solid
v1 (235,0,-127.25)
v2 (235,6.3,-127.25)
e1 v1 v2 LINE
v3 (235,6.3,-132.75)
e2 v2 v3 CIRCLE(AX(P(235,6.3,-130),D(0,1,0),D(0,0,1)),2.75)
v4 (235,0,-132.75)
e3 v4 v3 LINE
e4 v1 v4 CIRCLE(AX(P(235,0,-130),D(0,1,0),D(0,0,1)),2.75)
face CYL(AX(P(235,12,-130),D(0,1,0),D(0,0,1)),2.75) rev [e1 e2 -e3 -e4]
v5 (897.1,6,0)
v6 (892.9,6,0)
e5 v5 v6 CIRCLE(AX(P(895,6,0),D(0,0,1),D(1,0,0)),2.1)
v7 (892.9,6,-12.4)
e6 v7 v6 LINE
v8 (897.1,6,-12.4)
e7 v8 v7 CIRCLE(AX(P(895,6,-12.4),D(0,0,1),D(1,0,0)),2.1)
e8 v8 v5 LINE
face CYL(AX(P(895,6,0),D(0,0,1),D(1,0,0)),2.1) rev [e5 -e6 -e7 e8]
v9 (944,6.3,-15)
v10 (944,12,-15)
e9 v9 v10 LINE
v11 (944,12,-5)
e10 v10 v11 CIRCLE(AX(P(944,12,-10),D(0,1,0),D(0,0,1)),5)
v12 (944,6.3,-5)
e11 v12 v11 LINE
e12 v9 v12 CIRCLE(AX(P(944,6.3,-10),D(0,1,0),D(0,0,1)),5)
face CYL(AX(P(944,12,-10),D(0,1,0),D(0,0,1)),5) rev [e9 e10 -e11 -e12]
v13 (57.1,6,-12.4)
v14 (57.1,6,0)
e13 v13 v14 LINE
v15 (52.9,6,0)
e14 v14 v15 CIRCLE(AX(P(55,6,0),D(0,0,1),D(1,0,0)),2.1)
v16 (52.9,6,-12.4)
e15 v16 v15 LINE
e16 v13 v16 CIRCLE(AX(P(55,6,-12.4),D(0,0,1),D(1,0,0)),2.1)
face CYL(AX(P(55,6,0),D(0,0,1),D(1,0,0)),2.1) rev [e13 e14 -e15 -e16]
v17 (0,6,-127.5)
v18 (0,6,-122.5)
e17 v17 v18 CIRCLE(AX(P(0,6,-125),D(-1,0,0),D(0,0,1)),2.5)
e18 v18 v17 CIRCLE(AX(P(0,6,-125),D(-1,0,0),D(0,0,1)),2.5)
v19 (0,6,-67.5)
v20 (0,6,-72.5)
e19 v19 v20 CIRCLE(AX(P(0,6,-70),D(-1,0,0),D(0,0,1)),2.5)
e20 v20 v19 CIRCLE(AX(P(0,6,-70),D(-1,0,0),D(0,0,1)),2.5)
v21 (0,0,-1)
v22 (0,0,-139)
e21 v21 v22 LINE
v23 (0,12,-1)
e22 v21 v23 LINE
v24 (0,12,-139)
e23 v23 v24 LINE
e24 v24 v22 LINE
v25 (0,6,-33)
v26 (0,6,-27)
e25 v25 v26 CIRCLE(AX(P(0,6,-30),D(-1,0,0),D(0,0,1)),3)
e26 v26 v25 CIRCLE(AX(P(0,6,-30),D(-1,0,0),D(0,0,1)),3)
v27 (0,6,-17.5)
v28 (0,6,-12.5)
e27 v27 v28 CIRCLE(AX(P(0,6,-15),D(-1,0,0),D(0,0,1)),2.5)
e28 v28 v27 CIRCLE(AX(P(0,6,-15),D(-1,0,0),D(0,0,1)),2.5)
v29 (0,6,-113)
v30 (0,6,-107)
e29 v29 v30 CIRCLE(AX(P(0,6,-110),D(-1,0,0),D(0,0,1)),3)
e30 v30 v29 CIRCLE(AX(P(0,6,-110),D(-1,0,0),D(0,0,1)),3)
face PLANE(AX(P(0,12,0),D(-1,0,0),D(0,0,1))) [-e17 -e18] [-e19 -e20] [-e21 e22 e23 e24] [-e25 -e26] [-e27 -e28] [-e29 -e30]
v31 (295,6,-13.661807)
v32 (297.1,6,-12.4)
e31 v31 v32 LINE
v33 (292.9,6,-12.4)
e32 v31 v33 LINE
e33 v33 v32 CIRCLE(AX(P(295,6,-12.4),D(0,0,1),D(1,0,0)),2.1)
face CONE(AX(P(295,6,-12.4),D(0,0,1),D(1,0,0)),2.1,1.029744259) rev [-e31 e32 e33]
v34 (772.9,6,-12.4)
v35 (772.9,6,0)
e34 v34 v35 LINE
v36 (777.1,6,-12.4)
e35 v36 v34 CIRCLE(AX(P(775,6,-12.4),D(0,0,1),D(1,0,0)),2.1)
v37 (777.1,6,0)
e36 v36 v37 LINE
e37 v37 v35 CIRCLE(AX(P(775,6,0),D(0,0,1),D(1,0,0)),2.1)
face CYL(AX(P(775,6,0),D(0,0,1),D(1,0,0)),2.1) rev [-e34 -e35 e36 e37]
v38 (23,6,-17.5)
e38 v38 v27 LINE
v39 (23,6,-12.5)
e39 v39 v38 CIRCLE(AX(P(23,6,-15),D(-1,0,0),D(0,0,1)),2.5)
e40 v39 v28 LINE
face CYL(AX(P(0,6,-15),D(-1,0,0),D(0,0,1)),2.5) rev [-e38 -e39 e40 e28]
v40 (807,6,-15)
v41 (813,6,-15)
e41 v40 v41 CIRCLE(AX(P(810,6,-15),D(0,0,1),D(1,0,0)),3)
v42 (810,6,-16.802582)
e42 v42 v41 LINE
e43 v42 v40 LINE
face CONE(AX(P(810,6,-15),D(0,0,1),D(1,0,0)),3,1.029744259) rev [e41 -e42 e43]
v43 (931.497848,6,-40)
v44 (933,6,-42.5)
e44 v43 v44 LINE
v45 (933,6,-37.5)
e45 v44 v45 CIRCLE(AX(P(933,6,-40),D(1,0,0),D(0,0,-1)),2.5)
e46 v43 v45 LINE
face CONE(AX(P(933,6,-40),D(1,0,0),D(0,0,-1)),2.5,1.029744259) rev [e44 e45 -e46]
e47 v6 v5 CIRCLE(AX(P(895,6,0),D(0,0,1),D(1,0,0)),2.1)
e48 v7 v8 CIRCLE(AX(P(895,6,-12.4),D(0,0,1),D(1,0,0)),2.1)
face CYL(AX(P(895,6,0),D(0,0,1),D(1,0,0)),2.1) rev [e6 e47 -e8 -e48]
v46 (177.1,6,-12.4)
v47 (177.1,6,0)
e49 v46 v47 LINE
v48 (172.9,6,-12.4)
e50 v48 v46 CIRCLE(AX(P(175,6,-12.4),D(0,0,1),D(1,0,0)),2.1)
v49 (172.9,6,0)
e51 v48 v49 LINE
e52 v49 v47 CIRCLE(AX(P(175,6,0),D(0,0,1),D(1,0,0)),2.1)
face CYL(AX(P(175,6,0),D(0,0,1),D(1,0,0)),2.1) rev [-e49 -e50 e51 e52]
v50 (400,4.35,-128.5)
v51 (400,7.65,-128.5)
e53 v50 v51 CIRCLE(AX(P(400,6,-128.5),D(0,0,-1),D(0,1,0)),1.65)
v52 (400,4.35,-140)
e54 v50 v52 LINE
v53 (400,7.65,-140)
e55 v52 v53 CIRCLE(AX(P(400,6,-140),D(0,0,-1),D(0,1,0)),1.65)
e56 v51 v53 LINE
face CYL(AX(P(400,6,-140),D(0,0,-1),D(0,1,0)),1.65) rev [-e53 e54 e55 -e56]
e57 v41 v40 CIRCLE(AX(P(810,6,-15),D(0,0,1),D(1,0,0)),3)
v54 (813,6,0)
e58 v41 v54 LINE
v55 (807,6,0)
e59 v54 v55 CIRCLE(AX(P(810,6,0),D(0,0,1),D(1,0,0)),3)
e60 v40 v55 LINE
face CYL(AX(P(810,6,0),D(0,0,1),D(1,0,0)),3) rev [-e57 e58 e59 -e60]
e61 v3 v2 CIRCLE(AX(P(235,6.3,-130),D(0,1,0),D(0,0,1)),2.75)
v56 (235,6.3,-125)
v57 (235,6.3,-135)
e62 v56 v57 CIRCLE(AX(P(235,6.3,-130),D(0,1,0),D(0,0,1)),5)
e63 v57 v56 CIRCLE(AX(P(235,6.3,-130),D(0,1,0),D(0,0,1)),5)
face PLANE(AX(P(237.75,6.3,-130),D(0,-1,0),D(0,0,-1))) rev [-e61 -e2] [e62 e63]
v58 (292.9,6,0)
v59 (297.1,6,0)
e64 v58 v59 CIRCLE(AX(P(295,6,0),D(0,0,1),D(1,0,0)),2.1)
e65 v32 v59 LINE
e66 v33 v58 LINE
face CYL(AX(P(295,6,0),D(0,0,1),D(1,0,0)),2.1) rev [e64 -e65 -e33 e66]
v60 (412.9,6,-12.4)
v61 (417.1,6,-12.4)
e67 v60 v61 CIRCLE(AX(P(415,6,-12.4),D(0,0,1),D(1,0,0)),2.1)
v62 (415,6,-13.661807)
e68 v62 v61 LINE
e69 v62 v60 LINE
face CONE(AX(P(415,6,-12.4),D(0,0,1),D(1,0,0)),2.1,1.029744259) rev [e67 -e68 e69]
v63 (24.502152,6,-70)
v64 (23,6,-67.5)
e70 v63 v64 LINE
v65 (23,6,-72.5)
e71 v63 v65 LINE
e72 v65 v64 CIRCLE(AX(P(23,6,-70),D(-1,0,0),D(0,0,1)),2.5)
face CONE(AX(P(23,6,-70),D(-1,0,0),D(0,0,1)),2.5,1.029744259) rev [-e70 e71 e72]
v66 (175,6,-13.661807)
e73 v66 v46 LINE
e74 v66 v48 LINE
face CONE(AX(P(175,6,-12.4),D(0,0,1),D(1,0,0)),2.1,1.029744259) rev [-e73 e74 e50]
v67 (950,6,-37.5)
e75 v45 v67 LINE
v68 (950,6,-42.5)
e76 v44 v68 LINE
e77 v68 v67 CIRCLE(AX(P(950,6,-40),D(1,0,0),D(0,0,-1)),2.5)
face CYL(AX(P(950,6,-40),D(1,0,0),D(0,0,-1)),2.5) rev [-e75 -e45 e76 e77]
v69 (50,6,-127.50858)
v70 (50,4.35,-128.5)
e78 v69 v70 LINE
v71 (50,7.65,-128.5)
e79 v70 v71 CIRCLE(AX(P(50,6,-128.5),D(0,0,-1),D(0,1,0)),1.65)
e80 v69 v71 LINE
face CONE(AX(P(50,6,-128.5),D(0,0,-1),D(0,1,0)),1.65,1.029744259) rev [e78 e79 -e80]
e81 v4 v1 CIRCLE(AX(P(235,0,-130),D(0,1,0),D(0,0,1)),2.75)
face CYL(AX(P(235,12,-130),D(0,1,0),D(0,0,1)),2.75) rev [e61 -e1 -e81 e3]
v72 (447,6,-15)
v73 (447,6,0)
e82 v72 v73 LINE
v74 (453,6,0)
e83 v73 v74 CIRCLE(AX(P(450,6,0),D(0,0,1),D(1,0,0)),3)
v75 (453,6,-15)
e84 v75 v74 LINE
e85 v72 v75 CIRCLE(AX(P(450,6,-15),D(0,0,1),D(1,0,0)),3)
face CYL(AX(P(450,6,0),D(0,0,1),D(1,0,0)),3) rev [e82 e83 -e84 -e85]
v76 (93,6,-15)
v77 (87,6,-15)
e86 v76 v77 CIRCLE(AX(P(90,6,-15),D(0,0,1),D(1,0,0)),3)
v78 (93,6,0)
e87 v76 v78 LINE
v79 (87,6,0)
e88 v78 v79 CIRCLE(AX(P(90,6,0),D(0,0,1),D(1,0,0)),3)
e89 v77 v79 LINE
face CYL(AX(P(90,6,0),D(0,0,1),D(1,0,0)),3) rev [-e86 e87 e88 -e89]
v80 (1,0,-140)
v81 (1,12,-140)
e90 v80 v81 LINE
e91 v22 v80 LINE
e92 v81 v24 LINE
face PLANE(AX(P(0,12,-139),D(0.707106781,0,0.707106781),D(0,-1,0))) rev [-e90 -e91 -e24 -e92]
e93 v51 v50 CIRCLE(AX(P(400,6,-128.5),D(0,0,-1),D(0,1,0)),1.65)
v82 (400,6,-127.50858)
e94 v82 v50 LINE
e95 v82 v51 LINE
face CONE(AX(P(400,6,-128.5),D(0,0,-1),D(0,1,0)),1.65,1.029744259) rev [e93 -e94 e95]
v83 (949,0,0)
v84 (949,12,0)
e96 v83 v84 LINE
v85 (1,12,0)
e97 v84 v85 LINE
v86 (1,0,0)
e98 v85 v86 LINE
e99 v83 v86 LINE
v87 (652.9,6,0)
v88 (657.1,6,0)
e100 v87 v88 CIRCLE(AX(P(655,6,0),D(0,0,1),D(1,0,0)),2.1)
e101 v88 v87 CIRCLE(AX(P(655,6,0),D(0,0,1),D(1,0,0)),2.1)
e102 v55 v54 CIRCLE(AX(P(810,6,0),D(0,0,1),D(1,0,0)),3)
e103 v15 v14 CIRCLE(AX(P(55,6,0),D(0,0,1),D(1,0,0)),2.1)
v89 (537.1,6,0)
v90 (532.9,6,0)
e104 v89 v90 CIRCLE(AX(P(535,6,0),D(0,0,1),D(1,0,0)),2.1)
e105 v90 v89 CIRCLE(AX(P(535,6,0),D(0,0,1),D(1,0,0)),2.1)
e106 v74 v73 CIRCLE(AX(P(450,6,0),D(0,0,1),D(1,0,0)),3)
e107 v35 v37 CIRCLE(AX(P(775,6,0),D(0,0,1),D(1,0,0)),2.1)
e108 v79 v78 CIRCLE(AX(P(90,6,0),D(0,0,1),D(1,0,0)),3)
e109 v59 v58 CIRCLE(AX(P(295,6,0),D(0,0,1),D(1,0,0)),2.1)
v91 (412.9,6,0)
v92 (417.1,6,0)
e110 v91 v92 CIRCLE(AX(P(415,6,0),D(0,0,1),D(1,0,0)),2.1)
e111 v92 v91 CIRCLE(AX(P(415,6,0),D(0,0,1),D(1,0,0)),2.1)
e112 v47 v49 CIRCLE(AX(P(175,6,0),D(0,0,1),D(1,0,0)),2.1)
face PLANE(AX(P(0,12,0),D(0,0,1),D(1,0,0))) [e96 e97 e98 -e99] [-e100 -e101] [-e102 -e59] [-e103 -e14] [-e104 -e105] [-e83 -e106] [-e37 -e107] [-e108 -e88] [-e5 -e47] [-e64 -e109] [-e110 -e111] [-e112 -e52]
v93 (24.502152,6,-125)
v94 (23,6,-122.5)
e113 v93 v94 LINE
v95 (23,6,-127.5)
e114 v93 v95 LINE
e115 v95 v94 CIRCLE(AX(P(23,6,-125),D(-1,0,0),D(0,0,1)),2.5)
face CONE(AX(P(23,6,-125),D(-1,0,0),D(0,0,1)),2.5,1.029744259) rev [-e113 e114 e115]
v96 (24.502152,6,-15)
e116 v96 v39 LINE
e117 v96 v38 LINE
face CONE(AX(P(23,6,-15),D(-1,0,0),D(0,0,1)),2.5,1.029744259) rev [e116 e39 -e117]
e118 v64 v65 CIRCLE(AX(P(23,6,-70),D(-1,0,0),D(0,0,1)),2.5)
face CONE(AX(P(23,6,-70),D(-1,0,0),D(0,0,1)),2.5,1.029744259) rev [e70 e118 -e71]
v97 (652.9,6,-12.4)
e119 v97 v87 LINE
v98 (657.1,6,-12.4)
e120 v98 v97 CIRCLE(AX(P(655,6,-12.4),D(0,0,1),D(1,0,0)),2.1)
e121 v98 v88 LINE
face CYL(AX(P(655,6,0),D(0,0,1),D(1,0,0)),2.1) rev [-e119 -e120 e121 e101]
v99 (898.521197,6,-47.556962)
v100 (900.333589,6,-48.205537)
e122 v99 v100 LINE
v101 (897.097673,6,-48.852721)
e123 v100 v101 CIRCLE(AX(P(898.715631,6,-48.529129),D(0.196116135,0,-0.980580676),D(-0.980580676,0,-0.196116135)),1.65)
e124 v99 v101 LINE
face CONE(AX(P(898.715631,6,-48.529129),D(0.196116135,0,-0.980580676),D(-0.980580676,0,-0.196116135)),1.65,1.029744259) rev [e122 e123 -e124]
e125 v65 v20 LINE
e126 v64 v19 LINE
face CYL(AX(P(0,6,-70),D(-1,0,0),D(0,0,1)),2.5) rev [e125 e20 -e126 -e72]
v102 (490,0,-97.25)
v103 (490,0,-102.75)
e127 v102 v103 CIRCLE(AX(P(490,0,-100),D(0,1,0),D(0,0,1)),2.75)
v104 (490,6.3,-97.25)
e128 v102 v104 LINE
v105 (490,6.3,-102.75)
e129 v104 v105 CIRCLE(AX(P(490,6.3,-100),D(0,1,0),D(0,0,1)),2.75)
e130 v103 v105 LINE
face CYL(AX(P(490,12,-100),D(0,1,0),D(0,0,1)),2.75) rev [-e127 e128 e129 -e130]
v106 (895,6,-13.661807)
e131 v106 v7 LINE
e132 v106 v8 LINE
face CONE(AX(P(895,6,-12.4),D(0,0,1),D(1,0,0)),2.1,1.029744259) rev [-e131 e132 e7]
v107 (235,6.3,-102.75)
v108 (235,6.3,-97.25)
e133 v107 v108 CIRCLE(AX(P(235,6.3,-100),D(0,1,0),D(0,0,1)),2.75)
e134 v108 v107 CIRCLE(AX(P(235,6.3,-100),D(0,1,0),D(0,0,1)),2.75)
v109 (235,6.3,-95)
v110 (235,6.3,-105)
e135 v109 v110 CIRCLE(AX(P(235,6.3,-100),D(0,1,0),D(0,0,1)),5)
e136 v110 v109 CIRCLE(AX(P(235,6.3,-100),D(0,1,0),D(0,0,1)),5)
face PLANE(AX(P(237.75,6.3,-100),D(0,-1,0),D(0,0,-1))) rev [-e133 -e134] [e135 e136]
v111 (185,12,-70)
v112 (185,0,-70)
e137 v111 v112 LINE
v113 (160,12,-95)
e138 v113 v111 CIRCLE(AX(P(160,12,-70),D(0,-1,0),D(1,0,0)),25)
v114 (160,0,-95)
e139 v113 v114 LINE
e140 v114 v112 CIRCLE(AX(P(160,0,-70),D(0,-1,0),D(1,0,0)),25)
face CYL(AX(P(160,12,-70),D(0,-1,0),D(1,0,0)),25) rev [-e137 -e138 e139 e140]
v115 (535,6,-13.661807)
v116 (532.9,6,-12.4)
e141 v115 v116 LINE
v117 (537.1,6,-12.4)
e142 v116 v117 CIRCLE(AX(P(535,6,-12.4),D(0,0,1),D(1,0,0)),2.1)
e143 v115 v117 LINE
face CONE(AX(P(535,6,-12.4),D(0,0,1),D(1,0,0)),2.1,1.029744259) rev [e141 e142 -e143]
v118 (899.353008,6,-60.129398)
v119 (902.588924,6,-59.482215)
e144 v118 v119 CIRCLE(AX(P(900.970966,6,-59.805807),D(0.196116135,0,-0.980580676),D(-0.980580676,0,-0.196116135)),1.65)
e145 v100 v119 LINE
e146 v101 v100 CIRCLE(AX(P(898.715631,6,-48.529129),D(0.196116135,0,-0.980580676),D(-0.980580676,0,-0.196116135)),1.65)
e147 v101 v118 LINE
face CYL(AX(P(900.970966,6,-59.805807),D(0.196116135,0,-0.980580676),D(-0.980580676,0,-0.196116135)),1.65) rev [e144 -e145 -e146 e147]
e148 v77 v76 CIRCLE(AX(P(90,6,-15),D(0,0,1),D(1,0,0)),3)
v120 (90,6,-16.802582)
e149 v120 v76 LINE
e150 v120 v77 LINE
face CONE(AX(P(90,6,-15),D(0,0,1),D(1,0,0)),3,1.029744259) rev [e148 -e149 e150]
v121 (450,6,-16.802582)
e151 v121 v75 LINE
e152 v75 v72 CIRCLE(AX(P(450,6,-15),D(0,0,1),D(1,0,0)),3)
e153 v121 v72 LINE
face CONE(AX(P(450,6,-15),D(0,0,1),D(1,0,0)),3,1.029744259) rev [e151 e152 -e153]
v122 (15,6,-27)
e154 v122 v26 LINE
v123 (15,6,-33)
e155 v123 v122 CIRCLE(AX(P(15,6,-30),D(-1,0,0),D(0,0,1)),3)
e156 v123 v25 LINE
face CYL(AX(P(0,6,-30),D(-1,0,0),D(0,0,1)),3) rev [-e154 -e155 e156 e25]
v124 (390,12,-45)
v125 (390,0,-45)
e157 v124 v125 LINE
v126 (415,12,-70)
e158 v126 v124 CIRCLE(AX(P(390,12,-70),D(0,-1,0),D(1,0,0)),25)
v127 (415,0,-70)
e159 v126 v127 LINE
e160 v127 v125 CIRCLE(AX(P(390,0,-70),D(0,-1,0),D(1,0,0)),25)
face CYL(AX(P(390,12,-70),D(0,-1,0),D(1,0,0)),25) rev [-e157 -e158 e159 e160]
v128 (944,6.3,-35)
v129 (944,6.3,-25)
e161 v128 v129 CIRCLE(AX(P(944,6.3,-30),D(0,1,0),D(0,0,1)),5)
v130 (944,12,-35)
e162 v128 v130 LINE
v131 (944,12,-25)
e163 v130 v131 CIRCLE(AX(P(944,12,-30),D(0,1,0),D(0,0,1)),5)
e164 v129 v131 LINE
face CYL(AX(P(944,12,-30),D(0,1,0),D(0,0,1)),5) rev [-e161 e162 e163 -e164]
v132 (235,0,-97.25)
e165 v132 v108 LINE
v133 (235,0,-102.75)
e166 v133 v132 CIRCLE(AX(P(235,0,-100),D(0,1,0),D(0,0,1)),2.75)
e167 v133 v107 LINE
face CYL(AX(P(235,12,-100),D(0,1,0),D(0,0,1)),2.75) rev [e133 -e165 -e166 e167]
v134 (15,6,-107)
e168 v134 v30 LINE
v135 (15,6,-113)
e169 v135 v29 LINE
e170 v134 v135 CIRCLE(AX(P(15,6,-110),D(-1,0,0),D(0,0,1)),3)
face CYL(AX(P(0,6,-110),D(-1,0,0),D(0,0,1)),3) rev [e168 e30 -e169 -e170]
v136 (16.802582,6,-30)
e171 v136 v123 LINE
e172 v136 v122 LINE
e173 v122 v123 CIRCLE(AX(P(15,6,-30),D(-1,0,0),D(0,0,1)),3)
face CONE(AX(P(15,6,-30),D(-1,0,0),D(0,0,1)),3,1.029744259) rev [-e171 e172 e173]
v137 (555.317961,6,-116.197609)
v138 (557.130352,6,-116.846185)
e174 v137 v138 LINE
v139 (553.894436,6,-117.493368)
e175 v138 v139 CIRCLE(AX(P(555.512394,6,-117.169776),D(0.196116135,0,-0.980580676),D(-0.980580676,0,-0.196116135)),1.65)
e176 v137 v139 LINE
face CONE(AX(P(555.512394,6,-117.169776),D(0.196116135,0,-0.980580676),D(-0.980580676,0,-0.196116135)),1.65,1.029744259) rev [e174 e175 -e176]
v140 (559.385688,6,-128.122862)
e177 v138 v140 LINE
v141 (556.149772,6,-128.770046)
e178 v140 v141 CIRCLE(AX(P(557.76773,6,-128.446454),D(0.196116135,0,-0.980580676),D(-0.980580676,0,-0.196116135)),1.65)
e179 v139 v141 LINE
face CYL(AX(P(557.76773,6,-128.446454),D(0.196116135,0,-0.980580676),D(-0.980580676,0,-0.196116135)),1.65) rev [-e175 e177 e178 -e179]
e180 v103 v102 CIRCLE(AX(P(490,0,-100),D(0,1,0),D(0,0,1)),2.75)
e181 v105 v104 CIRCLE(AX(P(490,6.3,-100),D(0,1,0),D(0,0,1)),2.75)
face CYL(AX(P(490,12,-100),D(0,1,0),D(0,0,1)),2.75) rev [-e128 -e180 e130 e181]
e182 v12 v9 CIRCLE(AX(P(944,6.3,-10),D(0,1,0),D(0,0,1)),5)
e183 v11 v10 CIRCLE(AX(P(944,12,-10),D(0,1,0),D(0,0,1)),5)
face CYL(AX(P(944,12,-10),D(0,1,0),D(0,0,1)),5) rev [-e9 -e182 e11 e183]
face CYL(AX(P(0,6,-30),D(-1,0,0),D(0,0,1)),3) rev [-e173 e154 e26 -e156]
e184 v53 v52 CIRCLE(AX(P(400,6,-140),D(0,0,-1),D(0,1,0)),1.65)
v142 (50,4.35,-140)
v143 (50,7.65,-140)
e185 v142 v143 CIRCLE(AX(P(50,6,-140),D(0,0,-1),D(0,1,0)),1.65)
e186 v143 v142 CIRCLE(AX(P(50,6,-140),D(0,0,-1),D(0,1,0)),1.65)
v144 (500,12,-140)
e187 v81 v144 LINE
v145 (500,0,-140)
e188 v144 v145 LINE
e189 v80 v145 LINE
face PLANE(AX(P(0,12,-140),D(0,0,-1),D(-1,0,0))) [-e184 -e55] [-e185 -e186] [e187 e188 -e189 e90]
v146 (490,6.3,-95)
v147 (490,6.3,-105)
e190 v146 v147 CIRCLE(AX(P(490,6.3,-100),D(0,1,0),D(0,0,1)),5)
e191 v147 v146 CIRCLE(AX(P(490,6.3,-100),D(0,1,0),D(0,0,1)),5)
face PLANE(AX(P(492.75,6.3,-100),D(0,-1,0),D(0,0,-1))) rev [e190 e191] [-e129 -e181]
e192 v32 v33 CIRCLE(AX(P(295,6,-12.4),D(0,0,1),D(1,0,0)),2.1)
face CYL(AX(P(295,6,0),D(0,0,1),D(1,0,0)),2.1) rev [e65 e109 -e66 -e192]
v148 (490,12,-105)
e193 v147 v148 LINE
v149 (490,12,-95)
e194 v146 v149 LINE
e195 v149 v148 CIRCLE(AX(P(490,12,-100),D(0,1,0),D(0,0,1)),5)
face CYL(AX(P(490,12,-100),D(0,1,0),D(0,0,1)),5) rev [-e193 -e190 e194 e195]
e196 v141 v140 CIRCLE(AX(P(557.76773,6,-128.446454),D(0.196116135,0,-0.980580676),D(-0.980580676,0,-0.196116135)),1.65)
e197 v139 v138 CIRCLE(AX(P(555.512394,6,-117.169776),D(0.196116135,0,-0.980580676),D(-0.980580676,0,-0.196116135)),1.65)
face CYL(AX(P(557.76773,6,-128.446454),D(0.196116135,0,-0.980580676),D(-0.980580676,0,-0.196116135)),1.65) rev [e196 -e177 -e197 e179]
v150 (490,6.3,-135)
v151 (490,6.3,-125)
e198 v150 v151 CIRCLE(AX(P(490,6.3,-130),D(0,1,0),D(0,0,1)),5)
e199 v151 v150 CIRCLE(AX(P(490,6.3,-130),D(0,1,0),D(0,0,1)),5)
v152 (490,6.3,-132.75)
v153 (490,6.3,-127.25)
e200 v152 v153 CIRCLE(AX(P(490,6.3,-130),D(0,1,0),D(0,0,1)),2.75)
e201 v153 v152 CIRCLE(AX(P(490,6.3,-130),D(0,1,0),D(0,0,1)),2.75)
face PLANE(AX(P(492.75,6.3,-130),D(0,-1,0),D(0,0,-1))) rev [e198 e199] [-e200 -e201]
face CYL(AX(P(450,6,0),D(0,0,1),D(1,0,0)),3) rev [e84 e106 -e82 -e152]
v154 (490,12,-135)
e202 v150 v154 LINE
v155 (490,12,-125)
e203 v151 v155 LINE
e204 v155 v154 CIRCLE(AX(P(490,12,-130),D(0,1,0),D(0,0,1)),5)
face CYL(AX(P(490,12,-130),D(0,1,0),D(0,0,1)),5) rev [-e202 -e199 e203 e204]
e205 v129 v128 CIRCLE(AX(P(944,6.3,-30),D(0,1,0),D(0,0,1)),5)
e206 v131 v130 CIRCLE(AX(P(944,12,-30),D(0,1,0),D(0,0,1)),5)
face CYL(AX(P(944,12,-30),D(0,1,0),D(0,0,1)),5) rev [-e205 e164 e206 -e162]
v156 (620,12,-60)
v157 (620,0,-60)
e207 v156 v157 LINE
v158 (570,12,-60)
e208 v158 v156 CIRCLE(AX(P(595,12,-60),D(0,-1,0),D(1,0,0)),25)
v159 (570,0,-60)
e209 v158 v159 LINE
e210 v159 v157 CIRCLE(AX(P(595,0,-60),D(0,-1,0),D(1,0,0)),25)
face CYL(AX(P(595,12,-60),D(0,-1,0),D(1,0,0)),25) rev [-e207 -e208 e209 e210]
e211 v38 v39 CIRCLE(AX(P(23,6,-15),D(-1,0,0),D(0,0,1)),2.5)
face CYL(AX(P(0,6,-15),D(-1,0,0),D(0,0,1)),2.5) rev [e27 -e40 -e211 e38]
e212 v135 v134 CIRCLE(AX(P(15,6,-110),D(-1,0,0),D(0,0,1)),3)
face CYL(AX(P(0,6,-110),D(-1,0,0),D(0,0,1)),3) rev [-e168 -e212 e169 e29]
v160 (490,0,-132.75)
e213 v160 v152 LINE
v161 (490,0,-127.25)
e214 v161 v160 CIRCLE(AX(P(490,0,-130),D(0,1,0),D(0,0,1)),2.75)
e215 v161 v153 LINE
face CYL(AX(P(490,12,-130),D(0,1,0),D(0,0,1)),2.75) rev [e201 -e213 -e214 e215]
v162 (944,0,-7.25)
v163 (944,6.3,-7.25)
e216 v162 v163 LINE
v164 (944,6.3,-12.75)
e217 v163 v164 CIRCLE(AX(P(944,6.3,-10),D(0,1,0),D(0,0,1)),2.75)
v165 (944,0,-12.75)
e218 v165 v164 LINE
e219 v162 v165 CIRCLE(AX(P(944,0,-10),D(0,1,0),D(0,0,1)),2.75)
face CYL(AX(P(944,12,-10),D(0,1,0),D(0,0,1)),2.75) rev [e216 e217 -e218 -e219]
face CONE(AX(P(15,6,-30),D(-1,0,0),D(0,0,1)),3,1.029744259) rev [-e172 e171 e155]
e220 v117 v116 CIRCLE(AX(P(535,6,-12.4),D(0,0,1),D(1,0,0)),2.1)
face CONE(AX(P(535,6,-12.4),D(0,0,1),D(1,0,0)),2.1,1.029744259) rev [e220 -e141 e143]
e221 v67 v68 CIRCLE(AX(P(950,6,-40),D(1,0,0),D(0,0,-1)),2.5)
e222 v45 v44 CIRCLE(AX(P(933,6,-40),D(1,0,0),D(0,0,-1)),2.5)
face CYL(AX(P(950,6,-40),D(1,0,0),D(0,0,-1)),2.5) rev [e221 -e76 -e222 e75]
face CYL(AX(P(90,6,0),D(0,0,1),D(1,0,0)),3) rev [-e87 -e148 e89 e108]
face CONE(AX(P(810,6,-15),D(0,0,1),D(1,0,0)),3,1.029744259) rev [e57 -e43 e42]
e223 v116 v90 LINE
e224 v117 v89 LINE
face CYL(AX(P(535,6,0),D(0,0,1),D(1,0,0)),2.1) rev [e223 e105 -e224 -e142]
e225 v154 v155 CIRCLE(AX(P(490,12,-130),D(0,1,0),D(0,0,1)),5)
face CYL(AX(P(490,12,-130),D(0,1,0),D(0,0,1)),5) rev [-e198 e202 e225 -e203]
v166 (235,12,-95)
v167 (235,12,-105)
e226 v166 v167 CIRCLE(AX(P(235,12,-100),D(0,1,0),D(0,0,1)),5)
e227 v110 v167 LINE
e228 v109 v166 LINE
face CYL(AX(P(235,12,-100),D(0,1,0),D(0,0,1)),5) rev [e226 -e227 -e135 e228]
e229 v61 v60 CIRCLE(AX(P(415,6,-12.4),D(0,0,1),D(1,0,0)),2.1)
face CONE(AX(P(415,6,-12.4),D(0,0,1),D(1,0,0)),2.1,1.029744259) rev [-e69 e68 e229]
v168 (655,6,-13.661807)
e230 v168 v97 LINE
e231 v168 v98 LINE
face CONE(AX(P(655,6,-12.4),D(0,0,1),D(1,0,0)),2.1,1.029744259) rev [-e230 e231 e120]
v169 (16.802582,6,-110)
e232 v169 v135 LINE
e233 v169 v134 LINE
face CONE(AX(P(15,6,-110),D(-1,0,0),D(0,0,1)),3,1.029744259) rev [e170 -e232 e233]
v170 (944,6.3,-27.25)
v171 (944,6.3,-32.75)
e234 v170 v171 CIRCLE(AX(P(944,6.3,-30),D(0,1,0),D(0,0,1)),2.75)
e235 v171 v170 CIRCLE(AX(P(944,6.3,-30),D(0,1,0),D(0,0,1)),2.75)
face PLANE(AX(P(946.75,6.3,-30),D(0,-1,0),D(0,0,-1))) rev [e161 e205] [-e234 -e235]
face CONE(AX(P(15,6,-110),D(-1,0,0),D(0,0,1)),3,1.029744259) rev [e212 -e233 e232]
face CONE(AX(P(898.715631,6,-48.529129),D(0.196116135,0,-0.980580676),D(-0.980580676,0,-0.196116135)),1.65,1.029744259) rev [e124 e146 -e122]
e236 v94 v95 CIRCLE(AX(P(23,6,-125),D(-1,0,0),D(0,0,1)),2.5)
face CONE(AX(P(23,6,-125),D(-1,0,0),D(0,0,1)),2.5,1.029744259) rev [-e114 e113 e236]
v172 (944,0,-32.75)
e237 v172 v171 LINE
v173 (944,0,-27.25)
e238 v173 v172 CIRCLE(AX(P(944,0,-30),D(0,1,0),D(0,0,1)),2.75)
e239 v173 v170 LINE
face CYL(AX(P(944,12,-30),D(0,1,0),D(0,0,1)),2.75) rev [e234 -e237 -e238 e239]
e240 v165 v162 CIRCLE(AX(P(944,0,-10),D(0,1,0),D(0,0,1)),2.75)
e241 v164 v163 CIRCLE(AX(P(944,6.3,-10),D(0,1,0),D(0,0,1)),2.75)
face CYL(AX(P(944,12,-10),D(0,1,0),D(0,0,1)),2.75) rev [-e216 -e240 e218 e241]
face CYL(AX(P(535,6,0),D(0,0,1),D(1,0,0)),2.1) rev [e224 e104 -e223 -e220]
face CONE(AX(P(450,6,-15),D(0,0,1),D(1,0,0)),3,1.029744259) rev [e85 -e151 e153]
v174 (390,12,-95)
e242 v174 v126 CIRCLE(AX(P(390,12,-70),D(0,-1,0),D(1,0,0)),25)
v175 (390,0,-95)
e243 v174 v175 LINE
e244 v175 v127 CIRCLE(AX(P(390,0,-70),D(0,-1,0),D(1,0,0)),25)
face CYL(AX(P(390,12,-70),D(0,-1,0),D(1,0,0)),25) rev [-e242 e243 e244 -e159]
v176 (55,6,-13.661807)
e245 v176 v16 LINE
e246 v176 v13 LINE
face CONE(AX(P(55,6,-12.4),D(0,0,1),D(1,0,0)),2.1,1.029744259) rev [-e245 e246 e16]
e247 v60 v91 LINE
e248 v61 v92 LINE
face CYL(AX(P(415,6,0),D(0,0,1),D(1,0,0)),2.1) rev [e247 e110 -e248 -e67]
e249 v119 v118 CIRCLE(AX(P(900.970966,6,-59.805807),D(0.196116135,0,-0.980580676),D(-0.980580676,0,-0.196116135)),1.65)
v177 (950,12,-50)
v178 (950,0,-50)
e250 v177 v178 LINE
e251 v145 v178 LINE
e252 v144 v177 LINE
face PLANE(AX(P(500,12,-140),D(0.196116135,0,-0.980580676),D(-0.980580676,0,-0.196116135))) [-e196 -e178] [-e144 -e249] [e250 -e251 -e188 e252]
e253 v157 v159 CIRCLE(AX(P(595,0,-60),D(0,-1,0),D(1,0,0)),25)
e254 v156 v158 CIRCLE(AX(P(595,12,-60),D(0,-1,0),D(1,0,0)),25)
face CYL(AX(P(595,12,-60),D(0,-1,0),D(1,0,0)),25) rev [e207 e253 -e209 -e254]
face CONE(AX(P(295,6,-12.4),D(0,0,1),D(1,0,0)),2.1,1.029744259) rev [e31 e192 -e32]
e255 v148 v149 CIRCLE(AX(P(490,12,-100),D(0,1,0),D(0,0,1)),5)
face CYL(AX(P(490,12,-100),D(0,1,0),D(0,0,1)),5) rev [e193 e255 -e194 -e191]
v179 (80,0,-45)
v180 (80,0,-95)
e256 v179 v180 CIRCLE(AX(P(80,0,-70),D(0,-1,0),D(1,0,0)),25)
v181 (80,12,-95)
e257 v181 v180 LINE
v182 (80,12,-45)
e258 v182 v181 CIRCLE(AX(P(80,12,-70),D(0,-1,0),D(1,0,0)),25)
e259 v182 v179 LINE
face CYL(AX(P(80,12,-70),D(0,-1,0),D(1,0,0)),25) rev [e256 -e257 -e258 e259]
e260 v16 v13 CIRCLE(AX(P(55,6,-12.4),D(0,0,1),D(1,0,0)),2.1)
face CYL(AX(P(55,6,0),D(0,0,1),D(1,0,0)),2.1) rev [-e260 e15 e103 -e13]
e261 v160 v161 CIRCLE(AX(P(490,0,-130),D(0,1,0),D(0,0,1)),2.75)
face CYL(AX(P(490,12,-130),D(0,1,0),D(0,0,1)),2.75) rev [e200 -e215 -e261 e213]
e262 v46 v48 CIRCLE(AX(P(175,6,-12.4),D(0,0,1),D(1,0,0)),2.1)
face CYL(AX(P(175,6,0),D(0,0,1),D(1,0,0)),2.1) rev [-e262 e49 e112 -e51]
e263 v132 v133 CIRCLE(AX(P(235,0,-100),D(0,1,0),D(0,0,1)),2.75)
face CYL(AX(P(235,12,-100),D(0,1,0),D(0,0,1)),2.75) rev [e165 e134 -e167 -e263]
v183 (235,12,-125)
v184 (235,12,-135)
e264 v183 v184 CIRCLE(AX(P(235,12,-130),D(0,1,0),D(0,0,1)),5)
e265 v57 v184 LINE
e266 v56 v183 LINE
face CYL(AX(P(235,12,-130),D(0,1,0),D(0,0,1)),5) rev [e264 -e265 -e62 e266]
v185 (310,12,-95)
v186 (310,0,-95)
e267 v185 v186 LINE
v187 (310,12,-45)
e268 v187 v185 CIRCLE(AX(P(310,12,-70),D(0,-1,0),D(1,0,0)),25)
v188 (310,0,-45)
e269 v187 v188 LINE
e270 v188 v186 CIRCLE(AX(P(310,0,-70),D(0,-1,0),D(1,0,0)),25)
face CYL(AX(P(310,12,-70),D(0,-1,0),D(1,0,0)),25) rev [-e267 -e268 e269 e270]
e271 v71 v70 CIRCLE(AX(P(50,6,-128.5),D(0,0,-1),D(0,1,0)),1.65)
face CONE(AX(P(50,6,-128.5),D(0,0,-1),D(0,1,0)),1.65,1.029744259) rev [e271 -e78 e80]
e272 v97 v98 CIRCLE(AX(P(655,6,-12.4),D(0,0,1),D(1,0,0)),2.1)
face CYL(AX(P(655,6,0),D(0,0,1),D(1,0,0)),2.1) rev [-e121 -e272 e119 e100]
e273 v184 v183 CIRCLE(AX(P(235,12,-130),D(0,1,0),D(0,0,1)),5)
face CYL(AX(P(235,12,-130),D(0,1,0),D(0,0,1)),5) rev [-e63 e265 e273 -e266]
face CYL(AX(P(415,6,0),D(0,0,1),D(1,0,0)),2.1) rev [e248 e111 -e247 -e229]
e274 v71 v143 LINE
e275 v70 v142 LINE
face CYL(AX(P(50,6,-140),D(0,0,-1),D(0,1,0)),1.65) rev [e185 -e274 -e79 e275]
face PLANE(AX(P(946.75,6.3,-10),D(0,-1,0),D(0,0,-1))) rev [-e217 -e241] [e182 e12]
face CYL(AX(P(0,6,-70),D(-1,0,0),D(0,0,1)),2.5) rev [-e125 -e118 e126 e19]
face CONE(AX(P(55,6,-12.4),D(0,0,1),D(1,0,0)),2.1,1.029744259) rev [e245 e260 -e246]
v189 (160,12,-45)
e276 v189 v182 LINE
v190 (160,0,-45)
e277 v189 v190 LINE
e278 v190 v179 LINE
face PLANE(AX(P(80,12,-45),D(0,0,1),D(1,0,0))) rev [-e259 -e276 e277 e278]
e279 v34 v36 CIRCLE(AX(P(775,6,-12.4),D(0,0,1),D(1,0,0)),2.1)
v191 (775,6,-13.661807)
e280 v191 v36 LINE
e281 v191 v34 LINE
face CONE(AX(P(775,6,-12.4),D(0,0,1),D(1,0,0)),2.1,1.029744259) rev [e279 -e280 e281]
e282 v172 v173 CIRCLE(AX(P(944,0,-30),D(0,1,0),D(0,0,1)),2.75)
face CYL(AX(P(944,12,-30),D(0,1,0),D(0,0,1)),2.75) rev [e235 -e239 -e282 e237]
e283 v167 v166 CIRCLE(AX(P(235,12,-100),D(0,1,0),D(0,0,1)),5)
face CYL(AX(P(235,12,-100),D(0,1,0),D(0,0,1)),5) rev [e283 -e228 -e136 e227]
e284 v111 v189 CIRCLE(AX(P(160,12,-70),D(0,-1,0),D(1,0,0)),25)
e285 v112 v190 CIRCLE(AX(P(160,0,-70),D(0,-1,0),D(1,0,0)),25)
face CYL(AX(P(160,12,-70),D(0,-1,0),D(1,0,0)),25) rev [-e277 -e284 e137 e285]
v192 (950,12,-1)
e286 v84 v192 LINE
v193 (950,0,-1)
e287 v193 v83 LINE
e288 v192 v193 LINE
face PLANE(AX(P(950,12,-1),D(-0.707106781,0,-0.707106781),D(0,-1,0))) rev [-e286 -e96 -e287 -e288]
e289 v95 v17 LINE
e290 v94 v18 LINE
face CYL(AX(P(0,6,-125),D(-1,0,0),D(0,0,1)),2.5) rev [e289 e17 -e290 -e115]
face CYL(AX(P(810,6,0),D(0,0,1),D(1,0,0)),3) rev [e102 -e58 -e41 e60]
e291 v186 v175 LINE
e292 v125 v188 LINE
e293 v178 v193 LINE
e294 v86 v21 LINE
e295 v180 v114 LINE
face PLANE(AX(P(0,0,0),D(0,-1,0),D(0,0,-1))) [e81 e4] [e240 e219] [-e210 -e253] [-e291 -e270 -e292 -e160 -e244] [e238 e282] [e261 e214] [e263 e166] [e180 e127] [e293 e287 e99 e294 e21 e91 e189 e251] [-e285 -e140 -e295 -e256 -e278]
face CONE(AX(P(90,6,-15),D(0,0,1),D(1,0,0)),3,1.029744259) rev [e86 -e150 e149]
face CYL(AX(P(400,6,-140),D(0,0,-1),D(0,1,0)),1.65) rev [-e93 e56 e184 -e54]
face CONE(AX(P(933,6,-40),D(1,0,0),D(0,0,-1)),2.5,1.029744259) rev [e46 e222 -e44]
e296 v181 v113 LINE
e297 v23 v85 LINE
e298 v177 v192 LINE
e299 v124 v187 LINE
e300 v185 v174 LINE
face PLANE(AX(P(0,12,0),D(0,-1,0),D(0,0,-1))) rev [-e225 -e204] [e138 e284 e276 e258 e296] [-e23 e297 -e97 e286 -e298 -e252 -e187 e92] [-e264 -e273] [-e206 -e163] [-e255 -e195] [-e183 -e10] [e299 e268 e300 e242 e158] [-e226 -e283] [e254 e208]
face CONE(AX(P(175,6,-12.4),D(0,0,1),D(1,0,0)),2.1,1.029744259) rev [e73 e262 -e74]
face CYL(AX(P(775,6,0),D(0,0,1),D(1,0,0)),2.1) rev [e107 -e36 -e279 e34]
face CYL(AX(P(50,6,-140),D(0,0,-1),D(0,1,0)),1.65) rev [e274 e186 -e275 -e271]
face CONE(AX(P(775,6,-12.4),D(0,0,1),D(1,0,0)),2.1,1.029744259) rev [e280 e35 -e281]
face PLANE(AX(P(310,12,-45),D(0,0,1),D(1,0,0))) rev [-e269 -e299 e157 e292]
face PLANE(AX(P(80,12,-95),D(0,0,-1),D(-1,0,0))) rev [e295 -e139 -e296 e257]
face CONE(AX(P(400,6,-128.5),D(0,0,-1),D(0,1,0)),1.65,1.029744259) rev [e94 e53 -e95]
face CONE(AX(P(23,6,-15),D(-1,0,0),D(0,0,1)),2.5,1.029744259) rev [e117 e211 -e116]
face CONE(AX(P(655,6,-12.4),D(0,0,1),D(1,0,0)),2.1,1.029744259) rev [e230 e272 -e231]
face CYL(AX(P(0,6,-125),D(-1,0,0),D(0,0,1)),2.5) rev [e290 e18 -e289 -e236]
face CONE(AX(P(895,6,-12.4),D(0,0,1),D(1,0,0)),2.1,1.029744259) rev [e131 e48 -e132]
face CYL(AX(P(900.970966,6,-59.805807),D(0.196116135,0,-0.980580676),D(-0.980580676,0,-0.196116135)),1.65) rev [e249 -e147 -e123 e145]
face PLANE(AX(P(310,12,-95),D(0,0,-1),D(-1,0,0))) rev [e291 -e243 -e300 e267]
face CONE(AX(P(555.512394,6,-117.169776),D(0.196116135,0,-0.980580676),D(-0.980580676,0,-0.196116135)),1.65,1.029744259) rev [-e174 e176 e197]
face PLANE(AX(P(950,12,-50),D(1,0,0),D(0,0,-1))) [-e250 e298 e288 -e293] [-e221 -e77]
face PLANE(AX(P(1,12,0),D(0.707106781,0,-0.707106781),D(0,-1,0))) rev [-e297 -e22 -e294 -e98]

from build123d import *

# Parameters (mm, degrees)
BOSS_EXTRUDE2_DEPTH                              = 12
SKETCH9_R                                        = 25
CUT_EXTRUDE3_DEPTH                               = 12
M4_TAPPED_HOLE3_D                                = 3.3
M4_TAPPED_HOLE3_DEPTH                            = 11.5
M4_TAPPED_HOLE3_TIP                              = 0.991420021
M4_TAPPED_HOLE4_D                                = 3.3
M4_TAPPED_HOLE4_DEPTH                            = 11.5
M4_TAPPED_HOLE4_TIP                              = 0.991420021
M6_TAPPED_HOLE3_D                                = 5
M6_TAPPED_HOLE3_DEPTH                            = 17
M6_TAPPED_HOLE3_TIP                              = 1.502151548
M6_TAPPED_HOLE2_D                                = 5
M6_TAPPED_HOLE2_DEPTH                            = 23
M6_TAPPED_HOLE2_TIP                              = 1.502151548
F_6_0_6_DIAMETER_HOLE1_D                         = 6
F_6_0_6_DIAMETER_HOLE1_DEPTH                     = 15
F_6_0_6_DIAMETER_HOLE1_TIP                       = 1.802581857
M5_TAPPED_HOLE1_D                                = 4.2
M5_TAPPED_HOLE1_DEPTH                            = 12.4
M5_TAPPED_HOLE1_TIP                              = 1.2618073
F_6_0_6_DIAMETER_HOLE2_D                         = 6
F_6_0_6_DIAMETER_HOLE2_DEPTH                     = 15
F_6_0_6_DIAMETER_HOLE2_TIP                       = 1.802581857
HOLE_SIZE_PER_HEX_SOCKET_SCREW_TYPE1_D           = 5.5
HOLE_SIZE_PER_HEX_SOCKET_SCREW_TYPE1_CBORE_D     = 10
HOLE_SIZE_PER_HEX_SOCKET_SCREW_TYPE1_CBORE_DEPTH = 5.7
CHAMFER1_SIZE                                    = 1


with BuildPart() as part:
    # Sketch2 → Boss-Extrude2 (new body)
    with BuildSketch(Plane(origin=(0, 0, 0), x_dir=(-1, 0, 0), z_dir=(0, -1, 0))):
        Polygon((0, 0), (0, 140), (-500, 140), (-950, 50), (-950, 0), align=None)
    extrude(amount=-BOSS_EXTRUDE2_DEPTH)

    # Sketch9 → Cut-Extrude3 (cut)
    with BuildSketch(Plane.XZ):
        with Locations((595, -60)):
            Circle(SKETCH9_R)
        with BuildLine():
            Line((80, -45), (160, -45))
            ThreePointArc((160, -45), (185, -70), (160, -95))
            Line((160, -95), (80, -95))
            ThreePointArc((80, -95), (55, -70), (80, -45))
        make_face()
        with BuildLine():
            Line((310, -45), (390, -45))
            ThreePointArc((390, -45), (415, -70), (390, -95))
            Line((390, -95), (310, -95))
            ThreePointArc((310, -95), (285, -70), (310, -45))
        make_face()
    extrude(amount=-CUT_EXTRUDE3_DEPTH, mode=Mode.SUBTRACT)

    # M4 Tapped Hole3
    with Locations(Plane(origin=(0, 0, -140), x_dir=(-1, 0, 0), z_dir=(0, 0, -1))):
        with Locations((-50, 6), (-400, 6)):
            Hole(M4_TAPPED_HOLE3_D / 2, depth=M4_TAPPED_HOLE3_DEPTH)
            with Locations((0, 0, -(M4_TAPPED_HOLE3_DEPTH + M4_TAPPED_HOLE3_TIP / 2))):  # 118° drill point
                Cone(0, M4_TAPPED_HOLE3_D / 2, M4_TAPPED_HOLE3_TIP, mode=Mode.SUBTRACT)

    # M4 Tapped Hole4
    with Locations(Plane(origin=(46.153846154, 0, -230.769230769), x_dir=(-0.9805806756909201, 0, -0.19611613513818424), z_dir=(0.19611613513818424, 0, -0.9805806756909201))):
        with Locations((-871.745835149, 6), (-521.745835149, 6)):
            Hole(M4_TAPPED_HOLE4_D / 2, depth=M4_TAPPED_HOLE4_DEPTH)
            with Locations((0, 0, -(M4_TAPPED_HOLE4_DEPTH + M4_TAPPED_HOLE4_TIP / 2))):  # 118° drill point
                Cone(0, M4_TAPPED_HOLE4_D / 2, M4_TAPPED_HOLE4_TIP, mode=Mode.SUBTRACT)

    # M6 Tapped Hole3
    with Locations(Plane(origin=(950, 0, 0), x_dir=(0, 0, -1), z_dir=(1, 0, 0))):
        with Locations((40, 6), (40, 96)):
            Hole(M6_TAPPED_HOLE3_D / 2, depth=M6_TAPPED_HOLE3_DEPTH)
            with Locations((0, 0, -(M6_TAPPED_HOLE3_DEPTH + M6_TAPPED_HOLE3_TIP / 2))):  # 118° drill point
                Cone(0, M6_TAPPED_HOLE3_D / 2, M6_TAPPED_HOLE3_TIP, mode=Mode.SUBTRACT)

    # M6 Tapped Hole2
    with Locations(Plane.ZY):
        with Locations((-15, 6), (-70, 6), (-125, 6)):
            Hole(M6_TAPPED_HOLE2_D / 2, depth=M6_TAPPED_HOLE2_DEPTH)
            with Locations((0, 0, -(M6_TAPPED_HOLE2_DEPTH + M6_TAPPED_HOLE2_TIP / 2))):  # 118° drill point
                Cone(0, M6_TAPPED_HOLE2_D / 2, M6_TAPPED_HOLE2_TIP, mode=Mode.SUBTRACT)

    # Ø6.0 (6) Diameter Hole1
    with Locations(Plane.ZY):
        with Locations((-30, 6), (-110, 6)):
            Hole(F_6_0_6_DIAMETER_HOLE1_D / 2, depth=F_6_0_6_DIAMETER_HOLE1_DEPTH)
            with Locations((0, 0, -(F_6_0_6_DIAMETER_HOLE1_DEPTH + F_6_0_6_DIAMETER_HOLE1_TIP / 2))):  # 118° drill point
                Cone(0, F_6_0_6_DIAMETER_HOLE1_D / 2, F_6_0_6_DIAMETER_HOLE1_TIP, mode=Mode.SUBTRACT)

    # M5 Tapped Hole1
    with Locations(Plane.XY):
        with Locations((55, 6), (175, 6), (295, 6), (415, 6), (535, 6), (655, 6), (775, 6), (895, 6)):
            Hole(M5_TAPPED_HOLE1_D / 2, depth=M5_TAPPED_HOLE1_DEPTH)
            with Locations((0, 0, -(M5_TAPPED_HOLE1_DEPTH + M5_TAPPED_HOLE1_TIP / 2))):  # 118° drill point
                Cone(0, M5_TAPPED_HOLE1_D / 2, M5_TAPPED_HOLE1_TIP, mode=Mode.SUBTRACT)

    # Ø6.0 (6) Diameter Hole2
    with Locations(Plane.XY):
        with Locations((90, 6), (450, 6), (810, 6)):
            Hole(F_6_0_6_DIAMETER_HOLE2_D / 2, depth=F_6_0_6_DIAMETER_HOLE2_DEPTH)
            with Locations((0, 0, -(F_6_0_6_DIAMETER_HOLE2_DEPTH + F_6_0_6_DIAMETER_HOLE2_TIP / 2))):  # 118° drill point
                Cone(0, F_6_0_6_DIAMETER_HOLE2_D / 2, F_6_0_6_DIAMETER_HOLE2_TIP, mode=Mode.SUBTRACT)

    # Hole size per hex socket screw type1 (through all)
    with Locations(Plane(origin=(-526.958693224, 12, -55.479422486), x_dir=(-1, 0, 0), z_dir=(0, 1, 0))):
        with Locations((-761.958693224, -44.520577514), (-761.958693224, -74.520577514), (-1016.958693224, -44.520577514), (-1016.958693224, -74.520577514), (-1470.958693224, 45.479422486), (-1470.958693224, 25.479422486)):
            CounterBoreHole(HOLE_SIZE_PER_HEX_SOCKET_SCREW_TYPE1_D / 2, HOLE_SIZE_PER_HEX_SOCKET_SCREW_TYPE1_CBORE_D / 2, HOLE_SIZE_PER_HEX_SOCKET_SCREW_TYPE1_CBORE_DEPTH)

    # Chamfer1
    chamfer1_edges = [part.edges().sort_by_distance(p)[0] for p in [
        (950, 6, 0),
        (0, 6, -140),
        (0, 6, 0),
    ]]
    chamfer(chamfer1_edges, length=CHAMFER1_SIZE)


solid = part.part
